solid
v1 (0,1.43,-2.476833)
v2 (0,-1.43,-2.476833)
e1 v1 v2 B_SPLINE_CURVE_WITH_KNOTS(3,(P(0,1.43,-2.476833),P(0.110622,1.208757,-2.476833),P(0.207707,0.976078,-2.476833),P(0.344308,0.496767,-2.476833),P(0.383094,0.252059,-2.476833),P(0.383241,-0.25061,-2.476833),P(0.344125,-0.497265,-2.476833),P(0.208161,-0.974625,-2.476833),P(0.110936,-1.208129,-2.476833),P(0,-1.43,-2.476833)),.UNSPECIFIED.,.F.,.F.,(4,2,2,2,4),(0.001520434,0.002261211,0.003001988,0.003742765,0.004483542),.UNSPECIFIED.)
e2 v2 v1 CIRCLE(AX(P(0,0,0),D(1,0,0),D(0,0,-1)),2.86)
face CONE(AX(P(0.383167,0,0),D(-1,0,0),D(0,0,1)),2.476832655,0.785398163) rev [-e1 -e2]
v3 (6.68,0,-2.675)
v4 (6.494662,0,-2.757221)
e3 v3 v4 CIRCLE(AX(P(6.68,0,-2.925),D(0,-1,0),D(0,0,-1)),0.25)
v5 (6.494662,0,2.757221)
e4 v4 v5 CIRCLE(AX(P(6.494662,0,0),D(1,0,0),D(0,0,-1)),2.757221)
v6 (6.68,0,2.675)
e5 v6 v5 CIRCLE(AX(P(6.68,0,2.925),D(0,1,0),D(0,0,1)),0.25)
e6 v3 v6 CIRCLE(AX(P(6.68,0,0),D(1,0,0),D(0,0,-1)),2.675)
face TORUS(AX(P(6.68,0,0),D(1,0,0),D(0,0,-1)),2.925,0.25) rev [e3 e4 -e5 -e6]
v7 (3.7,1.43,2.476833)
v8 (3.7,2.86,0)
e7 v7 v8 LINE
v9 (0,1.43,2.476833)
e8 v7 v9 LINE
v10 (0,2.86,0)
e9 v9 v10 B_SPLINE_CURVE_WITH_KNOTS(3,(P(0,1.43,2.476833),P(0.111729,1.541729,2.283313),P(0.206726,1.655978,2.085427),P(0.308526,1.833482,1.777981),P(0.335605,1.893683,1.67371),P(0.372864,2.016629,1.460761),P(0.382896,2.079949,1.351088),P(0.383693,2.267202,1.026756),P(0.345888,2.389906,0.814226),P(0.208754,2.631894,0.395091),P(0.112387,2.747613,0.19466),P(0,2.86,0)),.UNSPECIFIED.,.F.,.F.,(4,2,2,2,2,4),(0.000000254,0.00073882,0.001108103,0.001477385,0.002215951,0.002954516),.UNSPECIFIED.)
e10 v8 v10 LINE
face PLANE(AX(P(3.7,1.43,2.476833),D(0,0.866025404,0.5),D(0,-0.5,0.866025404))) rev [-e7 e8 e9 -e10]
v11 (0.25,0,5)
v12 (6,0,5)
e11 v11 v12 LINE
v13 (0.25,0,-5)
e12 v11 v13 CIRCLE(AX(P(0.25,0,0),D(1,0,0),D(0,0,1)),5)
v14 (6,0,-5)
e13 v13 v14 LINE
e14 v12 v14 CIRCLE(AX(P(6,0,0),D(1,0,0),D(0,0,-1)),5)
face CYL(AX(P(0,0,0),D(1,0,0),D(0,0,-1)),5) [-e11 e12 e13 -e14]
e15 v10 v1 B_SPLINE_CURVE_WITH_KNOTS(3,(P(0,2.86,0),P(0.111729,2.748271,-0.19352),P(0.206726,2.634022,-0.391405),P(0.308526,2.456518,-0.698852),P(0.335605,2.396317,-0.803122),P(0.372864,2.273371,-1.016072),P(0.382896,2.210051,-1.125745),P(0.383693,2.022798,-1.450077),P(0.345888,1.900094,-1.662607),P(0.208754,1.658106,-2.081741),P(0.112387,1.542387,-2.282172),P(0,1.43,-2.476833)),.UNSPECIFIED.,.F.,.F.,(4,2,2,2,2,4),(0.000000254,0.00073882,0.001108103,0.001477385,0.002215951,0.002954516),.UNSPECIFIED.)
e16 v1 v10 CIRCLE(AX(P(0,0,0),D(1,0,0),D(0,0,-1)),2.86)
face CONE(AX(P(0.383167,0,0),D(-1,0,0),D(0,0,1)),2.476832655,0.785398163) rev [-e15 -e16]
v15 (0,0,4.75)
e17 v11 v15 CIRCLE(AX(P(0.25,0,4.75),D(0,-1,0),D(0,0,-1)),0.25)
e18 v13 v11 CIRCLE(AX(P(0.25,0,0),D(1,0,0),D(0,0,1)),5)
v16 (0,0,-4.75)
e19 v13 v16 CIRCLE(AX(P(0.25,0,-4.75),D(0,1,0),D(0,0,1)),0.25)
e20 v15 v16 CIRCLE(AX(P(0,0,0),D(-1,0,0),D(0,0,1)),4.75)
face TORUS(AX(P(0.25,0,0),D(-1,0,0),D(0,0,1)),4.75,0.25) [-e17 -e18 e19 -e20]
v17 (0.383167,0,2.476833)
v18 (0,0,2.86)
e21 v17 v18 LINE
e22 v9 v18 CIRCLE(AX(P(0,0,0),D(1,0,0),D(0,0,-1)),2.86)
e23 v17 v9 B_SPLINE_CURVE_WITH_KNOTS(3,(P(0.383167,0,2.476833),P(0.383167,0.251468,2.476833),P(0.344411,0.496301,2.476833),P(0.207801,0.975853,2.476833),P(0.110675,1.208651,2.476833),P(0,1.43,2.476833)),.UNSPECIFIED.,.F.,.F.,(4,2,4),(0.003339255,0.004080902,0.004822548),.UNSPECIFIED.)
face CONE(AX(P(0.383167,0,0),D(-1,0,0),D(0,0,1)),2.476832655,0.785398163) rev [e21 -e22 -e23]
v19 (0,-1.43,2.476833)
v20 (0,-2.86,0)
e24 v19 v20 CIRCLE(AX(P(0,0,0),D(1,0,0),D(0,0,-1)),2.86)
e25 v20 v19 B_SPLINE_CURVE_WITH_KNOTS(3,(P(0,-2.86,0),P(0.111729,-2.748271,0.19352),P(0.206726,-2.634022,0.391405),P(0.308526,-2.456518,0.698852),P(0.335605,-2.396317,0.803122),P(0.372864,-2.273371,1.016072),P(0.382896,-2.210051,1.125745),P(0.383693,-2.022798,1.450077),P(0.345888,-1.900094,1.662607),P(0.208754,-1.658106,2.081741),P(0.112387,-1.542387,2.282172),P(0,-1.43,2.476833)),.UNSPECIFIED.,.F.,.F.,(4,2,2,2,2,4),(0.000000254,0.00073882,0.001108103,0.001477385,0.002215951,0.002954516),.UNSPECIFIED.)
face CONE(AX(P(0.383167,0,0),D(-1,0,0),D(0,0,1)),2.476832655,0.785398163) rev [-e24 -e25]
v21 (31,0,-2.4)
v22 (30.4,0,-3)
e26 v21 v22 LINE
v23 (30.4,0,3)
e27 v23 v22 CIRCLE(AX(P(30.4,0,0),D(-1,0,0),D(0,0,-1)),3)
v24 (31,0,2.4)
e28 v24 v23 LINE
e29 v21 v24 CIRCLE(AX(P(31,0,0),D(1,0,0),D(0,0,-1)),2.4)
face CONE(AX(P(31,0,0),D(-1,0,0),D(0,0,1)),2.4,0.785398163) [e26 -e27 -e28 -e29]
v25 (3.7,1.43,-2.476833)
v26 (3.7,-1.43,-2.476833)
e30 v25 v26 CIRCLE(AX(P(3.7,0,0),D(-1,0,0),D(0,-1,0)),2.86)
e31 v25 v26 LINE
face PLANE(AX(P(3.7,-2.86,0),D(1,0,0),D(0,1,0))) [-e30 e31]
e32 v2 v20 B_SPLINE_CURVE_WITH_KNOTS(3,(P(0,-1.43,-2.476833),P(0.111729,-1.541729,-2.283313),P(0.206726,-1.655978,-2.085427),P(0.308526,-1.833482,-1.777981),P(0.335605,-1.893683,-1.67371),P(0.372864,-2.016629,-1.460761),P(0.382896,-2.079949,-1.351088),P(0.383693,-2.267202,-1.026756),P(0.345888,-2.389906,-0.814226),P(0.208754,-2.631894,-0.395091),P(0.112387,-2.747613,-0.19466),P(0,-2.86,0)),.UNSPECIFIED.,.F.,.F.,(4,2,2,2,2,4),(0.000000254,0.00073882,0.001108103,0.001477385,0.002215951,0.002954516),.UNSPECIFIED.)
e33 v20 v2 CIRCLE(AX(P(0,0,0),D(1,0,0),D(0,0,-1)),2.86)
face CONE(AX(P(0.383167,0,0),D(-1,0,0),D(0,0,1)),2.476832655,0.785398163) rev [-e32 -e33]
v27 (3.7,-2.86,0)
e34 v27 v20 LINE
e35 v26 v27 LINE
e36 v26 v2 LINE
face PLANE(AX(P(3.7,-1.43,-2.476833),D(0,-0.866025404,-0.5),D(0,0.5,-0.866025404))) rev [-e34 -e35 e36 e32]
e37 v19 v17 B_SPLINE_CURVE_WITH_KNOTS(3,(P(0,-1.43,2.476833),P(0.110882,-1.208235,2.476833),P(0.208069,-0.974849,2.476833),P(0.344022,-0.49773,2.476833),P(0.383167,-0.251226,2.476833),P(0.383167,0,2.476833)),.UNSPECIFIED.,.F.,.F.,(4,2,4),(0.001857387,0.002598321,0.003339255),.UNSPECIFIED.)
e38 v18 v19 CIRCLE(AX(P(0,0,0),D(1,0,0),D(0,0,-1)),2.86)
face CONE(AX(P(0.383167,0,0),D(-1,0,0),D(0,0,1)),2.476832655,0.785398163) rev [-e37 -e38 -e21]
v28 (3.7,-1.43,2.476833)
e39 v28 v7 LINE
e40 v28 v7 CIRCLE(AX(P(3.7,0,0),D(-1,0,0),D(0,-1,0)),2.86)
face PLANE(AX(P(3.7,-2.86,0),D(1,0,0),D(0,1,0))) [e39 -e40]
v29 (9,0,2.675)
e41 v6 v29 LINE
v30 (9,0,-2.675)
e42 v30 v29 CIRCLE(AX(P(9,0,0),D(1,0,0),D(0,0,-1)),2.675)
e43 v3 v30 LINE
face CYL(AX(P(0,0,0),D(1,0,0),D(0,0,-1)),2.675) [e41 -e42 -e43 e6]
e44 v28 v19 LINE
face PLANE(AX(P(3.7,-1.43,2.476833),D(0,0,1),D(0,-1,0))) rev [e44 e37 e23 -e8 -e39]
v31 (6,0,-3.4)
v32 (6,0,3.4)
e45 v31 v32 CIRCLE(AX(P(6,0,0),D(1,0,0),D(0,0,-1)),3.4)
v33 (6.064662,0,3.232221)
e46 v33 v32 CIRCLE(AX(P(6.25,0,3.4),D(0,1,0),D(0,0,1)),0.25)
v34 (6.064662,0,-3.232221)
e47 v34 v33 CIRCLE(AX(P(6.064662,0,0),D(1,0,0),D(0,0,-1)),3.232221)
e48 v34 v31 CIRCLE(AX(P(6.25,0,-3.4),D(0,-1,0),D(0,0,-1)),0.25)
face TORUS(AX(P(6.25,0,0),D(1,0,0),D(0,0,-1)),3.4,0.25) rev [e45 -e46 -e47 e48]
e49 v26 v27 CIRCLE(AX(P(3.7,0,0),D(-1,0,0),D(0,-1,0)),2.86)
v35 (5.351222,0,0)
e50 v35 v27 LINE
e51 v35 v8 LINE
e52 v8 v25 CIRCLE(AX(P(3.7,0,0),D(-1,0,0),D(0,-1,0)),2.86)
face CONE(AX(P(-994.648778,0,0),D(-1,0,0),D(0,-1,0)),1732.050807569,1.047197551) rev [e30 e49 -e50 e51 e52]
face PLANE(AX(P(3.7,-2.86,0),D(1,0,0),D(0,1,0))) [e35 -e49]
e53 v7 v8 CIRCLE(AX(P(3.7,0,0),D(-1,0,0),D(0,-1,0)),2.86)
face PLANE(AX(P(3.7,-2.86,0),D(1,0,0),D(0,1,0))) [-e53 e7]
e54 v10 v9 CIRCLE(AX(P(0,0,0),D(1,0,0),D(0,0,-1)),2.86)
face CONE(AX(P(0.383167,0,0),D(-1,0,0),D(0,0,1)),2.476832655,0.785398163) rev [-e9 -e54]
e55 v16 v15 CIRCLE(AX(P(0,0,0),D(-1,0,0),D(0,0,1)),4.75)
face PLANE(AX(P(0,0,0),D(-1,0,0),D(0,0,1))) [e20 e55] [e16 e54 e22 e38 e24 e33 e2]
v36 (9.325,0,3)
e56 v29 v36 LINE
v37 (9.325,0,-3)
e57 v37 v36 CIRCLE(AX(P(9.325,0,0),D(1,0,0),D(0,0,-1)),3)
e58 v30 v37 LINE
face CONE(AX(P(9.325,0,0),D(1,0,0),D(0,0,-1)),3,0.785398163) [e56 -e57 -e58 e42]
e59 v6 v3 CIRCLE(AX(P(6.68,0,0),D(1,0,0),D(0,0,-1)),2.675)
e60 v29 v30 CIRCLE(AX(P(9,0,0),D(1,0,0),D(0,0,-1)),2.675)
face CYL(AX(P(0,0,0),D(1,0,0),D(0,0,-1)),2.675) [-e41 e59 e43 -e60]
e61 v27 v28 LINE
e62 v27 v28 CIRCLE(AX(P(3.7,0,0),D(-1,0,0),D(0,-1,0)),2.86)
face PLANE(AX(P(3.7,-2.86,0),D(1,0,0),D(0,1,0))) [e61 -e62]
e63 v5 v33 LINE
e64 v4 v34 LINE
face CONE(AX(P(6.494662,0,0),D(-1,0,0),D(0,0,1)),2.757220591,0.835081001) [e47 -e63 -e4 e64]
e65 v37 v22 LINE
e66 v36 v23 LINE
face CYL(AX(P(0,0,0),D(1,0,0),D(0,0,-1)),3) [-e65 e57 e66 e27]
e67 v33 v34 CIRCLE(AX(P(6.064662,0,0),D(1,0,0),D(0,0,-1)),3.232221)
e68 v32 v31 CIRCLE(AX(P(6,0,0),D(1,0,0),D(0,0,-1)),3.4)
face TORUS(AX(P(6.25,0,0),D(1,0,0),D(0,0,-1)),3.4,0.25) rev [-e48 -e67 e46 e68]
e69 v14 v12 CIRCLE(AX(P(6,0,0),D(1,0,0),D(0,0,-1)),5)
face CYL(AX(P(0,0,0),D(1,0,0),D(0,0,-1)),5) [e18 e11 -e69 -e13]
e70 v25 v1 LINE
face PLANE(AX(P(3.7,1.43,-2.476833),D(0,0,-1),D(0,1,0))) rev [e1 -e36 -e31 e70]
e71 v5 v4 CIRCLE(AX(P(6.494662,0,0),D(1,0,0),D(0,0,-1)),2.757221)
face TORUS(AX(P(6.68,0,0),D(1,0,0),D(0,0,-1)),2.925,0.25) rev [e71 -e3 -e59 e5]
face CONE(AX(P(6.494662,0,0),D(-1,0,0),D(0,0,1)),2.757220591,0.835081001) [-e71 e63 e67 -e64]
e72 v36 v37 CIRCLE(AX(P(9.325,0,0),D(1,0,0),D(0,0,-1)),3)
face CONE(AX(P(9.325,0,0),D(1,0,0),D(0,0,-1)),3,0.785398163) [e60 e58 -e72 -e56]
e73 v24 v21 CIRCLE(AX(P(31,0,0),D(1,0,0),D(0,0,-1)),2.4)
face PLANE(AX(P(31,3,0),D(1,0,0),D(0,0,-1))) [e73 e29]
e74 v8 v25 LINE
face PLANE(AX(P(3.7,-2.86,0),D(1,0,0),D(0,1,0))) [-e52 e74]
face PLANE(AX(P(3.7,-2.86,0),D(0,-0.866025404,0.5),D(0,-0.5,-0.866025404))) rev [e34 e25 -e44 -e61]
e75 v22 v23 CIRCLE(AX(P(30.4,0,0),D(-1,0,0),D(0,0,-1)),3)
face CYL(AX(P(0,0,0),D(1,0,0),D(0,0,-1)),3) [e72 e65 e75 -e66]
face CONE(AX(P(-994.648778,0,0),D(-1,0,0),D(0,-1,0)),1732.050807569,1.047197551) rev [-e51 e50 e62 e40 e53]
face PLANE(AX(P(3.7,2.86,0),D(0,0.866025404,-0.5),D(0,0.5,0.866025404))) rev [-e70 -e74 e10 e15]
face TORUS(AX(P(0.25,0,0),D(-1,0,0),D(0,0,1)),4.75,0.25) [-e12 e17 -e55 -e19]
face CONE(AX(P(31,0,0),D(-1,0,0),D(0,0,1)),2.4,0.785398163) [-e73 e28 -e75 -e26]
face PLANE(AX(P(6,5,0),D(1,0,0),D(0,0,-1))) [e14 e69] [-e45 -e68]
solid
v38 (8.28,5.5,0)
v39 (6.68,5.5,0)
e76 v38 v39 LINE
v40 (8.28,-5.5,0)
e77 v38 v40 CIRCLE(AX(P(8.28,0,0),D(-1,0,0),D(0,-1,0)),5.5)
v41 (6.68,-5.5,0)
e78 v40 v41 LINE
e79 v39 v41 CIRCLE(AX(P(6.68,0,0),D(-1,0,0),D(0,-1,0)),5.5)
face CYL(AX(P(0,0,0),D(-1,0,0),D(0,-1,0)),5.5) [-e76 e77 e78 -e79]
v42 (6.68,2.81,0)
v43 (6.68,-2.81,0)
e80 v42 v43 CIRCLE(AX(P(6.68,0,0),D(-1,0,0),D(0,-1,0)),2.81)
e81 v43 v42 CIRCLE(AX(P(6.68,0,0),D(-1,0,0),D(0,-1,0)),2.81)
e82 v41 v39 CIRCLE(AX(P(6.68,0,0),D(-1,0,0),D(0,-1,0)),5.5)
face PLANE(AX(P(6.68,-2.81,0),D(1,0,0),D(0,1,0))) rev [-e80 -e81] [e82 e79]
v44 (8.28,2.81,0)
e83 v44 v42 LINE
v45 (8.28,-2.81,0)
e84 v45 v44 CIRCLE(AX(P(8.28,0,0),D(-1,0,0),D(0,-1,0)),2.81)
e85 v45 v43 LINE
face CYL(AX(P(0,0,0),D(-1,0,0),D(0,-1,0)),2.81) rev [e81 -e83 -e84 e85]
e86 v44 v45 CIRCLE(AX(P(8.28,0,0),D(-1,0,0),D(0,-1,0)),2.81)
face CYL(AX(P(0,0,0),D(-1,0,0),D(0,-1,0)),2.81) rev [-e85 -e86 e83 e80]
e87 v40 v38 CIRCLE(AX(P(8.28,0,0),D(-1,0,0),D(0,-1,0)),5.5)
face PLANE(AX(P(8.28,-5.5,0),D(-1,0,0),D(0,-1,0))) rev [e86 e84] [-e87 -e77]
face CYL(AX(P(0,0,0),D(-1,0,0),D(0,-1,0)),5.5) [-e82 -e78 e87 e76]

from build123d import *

# Parameters (mm, degrees)
CUT_EXTRUDE1_DEPTH = 3.7
FILLET1_R          = 0.25
SKETCH11_W         = 1.6
SKETCH11_H         = 2.69
CHAMFER1_SIZE      = 0.6


with BuildPart() as part:
    # Sketch1 → Base-Revolve (revolve)
    with BuildSketch(Plane.XY, mode=Mode.PRIVATE) as base_revolve_sk:
        with BuildLine():
            Line((0, 0), (0, 5))
            Line((0, 5), (6, 5))
            Line((6, 5), (6, 3.4))
            ThreePointArc((6, 3.4), (6.016725023, 3.310095689), (6.064662281, 3.232220591))
            Line((6.064662281, 3.232220591), (6.494662281, 2.757220591))
            ThreePointArc((6.494662281, 2.757220591), (6.57862163, 2.696477734), (6.68, 2.675))
            Line((6.68, 2.675), (9, 2.675))
            Line((9, 2.675), (9.325, 3))
            Line((9.325, 3), (31, 3))
            Line((31, 3), (31, 0))
            Line((31, 0), (0, 0))
        make_face()
    revolve(base_revolve_sk.sketch.rotate(Axis((0, 0, 0), (-1, 0, 0)), 90), axis=Axis((0, 0, 0), (-1, 0, 0)))

    # Sketch2 → Cut-Extrude1 (cut)
    with BuildSketch(Plane.ZY):
        Polygon((2.476832655, -1.43), (2.476832655, 1.43), (0, 2.86), (-2.476832655, 1.43), (-2.476832655, -1.43), (0, -2.86), align=None)
    extrude(amount=-CUT_EXTRUDE1_DEPTH, mode=Mode.SUBTRACT)

    # Sketch13 → Cut-Revolve4 (revolve, cut)
    with BuildSketch(Plane.XY):
        Polygon((0, 2.86), (0.383167345, 2.476832655), (0, 2.476832655), align=None)
    revolve(axis=Axis((0, 0, 0), (-1, 0, 0)), mode=Mode.SUBTRACT)

    # Sketch16 → Cut-Revolve5 (revolve, cut)
    with BuildSketch(Plane.XY, mode=Mode.PRIVATE) as cut_revolve5_sk:
        Polygon((5.35122177, 0), (3.7, 2.86), (3.7, 0), align=None)
    revolve(cut_revolve5_sk.sketch.rotate(Axis((3.7, 0, 0), (1, 0, 0)), 180), axis=Axis((3.7, 0, 0), (1, 0, 0)), mode=Mode.SUBTRACT)

    # Fillet1
    fillet1_edges = [part.edges().sort_by_distance(p)[0] for p in [
        (0, 0, 5),
    ]]
    fillet(fillet1_edges, radius=FILLET1_R)

    # Chamfer1
    chamfer1_edges = [part.edges().sort_by_distance(p)[0] for p in [
        (31, 0, 3),
    ]]
    chamfer(chamfer1_edges, length=CHAMFER1_SIZE)


with BuildPart() as body_2:
    # Sketch11 → Revolve1 (revolve)
    with BuildSketch(Plane.XY, mode=Mode.PRIVATE) as revolve1_sk:
        with Locations((7.48, 4.155)):
            Rectangle(SKETCH11_W, SKETCH11_H)
    revolve(revolve1_sk.sketch.rotate(Axis((0, 0, 0), (1, 0, 0)), 180), axis=Axis((0, 0, 0), (1, 0, 0)))


solid = Compound([part.part, body_2.part])
